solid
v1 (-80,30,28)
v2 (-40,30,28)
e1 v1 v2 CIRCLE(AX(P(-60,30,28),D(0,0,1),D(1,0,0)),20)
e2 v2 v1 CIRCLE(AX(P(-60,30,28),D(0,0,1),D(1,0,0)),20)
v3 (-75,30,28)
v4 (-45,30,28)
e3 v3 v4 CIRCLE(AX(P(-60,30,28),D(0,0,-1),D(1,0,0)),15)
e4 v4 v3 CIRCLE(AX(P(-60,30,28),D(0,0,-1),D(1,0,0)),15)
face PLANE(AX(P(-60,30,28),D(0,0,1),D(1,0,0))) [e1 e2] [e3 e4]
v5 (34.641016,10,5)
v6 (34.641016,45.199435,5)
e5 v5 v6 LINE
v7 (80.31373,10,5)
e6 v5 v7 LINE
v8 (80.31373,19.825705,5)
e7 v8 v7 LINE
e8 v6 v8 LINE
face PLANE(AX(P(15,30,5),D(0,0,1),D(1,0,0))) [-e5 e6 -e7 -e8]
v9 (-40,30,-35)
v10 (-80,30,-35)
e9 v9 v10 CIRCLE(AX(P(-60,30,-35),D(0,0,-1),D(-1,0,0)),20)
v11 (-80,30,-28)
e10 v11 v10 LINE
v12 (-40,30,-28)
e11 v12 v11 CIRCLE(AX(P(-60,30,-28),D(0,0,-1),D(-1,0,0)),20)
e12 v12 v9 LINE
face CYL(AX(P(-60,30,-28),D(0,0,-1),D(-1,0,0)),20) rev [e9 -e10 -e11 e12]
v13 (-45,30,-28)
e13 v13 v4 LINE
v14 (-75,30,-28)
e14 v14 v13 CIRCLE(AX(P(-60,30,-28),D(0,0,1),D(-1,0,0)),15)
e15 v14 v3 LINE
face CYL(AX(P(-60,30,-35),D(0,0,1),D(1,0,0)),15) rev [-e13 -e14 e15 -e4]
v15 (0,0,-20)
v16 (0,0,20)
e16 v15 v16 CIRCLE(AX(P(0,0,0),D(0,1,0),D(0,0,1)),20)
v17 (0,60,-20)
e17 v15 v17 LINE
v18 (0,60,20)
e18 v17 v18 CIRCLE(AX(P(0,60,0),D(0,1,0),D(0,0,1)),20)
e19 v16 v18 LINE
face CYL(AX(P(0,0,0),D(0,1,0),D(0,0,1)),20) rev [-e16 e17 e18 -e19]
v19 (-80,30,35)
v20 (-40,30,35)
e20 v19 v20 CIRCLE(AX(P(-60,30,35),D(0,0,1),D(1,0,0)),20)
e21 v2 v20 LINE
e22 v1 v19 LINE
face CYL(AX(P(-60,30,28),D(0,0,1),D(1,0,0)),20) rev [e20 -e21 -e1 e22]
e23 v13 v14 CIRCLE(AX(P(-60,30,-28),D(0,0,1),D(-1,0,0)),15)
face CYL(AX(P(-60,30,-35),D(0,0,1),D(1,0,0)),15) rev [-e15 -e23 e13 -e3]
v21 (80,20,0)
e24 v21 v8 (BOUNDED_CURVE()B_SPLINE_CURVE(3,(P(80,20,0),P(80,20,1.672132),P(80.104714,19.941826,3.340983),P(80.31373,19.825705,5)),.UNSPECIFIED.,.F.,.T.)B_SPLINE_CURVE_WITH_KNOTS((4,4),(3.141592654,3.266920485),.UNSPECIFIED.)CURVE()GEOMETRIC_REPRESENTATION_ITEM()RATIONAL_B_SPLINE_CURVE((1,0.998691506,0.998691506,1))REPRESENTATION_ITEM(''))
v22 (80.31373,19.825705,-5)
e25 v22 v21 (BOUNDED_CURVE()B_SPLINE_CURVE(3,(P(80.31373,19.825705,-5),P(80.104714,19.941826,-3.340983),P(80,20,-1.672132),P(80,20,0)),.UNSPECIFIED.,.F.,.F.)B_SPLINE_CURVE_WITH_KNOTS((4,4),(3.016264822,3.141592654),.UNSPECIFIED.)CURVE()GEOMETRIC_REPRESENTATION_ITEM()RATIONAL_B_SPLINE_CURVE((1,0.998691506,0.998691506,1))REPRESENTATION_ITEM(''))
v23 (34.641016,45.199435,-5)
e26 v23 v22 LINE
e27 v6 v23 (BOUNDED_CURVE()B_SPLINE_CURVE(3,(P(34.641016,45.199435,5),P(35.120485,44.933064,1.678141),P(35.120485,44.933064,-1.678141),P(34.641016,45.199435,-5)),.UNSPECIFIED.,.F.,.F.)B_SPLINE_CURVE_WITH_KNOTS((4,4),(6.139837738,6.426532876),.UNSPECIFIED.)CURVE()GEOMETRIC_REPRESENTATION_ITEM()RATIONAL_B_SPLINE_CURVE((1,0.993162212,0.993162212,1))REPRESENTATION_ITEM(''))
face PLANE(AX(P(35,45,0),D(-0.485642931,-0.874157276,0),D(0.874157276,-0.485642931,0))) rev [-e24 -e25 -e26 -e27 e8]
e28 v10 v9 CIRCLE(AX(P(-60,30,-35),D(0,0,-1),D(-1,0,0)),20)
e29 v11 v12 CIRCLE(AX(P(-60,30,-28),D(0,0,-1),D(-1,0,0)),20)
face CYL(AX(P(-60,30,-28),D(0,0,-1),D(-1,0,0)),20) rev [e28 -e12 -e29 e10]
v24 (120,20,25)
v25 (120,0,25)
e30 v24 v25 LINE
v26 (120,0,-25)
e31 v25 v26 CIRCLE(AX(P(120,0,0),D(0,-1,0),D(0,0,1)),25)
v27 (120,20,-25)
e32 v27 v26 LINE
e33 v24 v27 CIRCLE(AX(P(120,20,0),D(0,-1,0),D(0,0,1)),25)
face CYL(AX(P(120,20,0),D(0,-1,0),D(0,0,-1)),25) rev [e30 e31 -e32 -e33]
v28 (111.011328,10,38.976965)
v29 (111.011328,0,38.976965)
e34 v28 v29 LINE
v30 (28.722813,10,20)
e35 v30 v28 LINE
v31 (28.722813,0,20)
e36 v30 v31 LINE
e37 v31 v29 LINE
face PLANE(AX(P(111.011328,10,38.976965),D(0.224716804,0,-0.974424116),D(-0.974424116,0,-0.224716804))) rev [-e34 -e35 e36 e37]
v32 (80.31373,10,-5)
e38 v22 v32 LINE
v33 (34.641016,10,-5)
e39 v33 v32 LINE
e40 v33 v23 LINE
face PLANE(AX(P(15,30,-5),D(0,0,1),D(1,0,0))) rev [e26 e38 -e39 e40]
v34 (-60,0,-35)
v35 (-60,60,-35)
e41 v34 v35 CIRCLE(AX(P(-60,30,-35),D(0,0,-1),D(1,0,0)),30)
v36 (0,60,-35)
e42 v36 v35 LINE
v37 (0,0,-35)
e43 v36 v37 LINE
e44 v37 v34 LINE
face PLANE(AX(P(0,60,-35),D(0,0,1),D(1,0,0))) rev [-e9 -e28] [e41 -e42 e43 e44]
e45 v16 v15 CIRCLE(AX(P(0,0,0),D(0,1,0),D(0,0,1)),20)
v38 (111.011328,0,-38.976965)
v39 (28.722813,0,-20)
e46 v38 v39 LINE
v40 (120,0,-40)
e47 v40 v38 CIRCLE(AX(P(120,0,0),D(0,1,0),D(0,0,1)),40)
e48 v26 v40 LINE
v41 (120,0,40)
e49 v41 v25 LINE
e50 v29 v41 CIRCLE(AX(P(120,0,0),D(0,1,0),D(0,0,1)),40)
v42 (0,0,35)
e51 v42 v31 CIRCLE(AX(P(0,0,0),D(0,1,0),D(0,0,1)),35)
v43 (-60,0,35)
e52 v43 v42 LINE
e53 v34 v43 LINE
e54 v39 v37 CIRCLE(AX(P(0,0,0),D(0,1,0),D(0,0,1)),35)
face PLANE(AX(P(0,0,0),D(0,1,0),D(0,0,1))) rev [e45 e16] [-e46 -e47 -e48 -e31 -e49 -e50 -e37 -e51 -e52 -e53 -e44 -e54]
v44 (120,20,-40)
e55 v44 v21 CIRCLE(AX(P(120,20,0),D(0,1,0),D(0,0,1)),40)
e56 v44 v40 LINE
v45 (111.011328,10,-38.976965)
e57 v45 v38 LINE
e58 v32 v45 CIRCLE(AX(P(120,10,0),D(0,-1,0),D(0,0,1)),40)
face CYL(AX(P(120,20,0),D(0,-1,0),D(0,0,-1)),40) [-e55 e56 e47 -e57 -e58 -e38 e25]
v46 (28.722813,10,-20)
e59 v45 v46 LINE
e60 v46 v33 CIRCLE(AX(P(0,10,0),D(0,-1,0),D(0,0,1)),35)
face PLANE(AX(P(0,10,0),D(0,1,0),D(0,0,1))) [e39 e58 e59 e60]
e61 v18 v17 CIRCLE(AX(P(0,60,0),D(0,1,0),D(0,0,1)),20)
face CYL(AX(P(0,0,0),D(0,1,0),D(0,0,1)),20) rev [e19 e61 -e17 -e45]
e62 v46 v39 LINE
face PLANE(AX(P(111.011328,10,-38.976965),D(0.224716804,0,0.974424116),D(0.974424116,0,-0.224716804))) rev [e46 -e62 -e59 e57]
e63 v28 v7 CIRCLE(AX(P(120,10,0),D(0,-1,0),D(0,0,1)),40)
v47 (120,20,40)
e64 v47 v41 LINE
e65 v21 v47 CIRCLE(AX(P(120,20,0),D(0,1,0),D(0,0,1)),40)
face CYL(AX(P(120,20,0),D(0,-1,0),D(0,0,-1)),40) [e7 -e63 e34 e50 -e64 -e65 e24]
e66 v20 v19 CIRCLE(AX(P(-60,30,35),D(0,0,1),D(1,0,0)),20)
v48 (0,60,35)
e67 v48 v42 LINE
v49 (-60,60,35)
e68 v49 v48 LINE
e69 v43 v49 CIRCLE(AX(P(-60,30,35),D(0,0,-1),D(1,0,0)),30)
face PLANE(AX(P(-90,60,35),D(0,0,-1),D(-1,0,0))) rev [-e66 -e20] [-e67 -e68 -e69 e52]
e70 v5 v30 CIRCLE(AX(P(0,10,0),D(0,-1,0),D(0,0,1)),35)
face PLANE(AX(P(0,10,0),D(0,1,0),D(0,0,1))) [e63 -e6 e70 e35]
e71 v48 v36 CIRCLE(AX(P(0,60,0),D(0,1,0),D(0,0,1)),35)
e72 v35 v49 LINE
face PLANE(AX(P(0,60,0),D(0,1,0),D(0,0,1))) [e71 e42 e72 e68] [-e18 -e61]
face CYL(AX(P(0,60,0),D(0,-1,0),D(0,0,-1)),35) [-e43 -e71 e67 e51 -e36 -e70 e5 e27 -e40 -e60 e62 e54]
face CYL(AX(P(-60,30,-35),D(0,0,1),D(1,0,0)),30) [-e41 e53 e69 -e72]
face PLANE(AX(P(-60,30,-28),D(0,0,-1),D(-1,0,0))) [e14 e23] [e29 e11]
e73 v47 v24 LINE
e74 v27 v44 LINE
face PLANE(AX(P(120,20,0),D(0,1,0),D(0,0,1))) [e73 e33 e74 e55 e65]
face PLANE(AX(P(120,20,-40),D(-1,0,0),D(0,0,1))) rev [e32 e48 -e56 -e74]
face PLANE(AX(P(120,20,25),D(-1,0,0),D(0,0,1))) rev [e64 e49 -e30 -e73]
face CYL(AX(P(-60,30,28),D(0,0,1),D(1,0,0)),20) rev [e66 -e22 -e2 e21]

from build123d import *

# Parameters (mm, degrees)
BASE_BLOCK_DEPTH              = 60
BLOCK_SIDE_PROFILE_CUT_DEPTH  = 129.840987267
VERTICAL_BORE_SKETCH_R        = 20
VERTICAL_BORE_40_DEPTH        = 114.688170009
HORIZONTAL_BORE_SKETCH_R      = 15
HORIZONTAL_BORE_30_DEPTH      = 129.840987267
COUNTERBORE_SIDE_A_SKETCH_R   = 20
COUNTERBORE_SIDE_A_40X7_DEPTH = 7
COUNTERBORE_START             = -7
COUNTERBORE_SIDE_B_SKETCH_R   = 20
COUNTERBORE_SIDE_B_40X7_DEPTH = 7
FORK_ARM_DEPTH                = 20
ARM_WEB_PLATE_DEPTH           = 10
ARM_RIB_REACH                 = 142
ARM_RIB_SKETCH_WALL_W         = 333.478150704
ARM_RIB_SKETCH_WALL_H         = 10


with BuildPart() as part:
    # Base Block Sketch → Base Block (new body)
    with BuildSketch(Plane(origin=(0, 0, 0), x_dir=(1, 0, 0), z_dir=(0, 1, 0))):
        with BuildLine():
            Line((0, 35), (-90, 35))
            Line((-90, 35), (-90, -35))
            Line((-90, -35), (0, -35))
            ThreePointArc((0, -35), (35, 0), (0, 35))
        make_face()
    extrude(amount=BASE_BLOCK_DEPTH)

    # Block Side Profile Sketch → Block Side Profile Cut (cut, through all)
    with BuildSketch(Plane.XY.offset(35)):
        with BuildLine():
            Line((-60, 60), (-120, 60))
            Line((-120, 60), (-120, 0))
            Line((-120, 0), (-60, 0))
            ThreePointArc((-60, 0), (-90, 30), (-60, 60))
        make_face()
    extrude(amount=-BLOCK_SIDE_PROFILE_CUT_DEPTH, mode=Mode.SUBTRACT)

    # Vertical Bore Sketch → Vertical Bore Ø40 (cut, through all)
    with BuildSketch(Plane(origin=(0, 60, 0), x_dir=(1, 0, 0), z_dir=(0, 1, 0))):
        with Locations(Location((0, 0, 0), (0, 0, 270))):
            Circle(VERTICAL_BORE_SKETCH_R)
    extrude(amount=-VERTICAL_BORE_40_DEPTH, mode=Mode.SUBTRACT)

    # Horizontal Bore Sketch → Horizontal Bore Ø30 (cut, through all)
    with BuildSketch(Plane.XY.offset(35)):
        with Locations((-60, 30)):
            Circle(HORIZONTAL_BORE_SKETCH_R)
    extrude(amount=-HORIZONTAL_BORE_30_DEPTH, mode=Mode.SUBTRACT)

    # Counterbore Side A Sketch → Counterbore Side A Ø40x7 (cut)
    with BuildSketch(Plane.XY.offset(35)):
        with Locations((-60, 30)):
            Circle(COUNTERBORE_SIDE_A_SKETCH_R)
    extrude(amount=-COUNTERBORE_SIDE_A_40X7_DEPTH, mode=Mode.SUBTRACT)

    # Counterbore Side B Sketch → Counterbore Side B Ø40x7 (cut)
    with BuildSketch(Plane(origin=(0, 0, -35), x_dir=(-1, 0, 0), z_dir=(0, 0, -1)).offset(COUNTERBORE_START)):
        with Locations(Location((60, 30, 0), (0, 0, 180))):
            Circle(COUNTERBORE_SIDE_B_SKETCH_R)
    extrude(amount=COUNTERBORE_SIDE_B_40X7_DEPTH, mode=Mode.SUBTRACT)



with BuildPart() as body_2:
    # Fork Arm Sketch → Fork Arm (new body)
    with BuildSketch(Plane(origin=(0, 0, 0), x_dir=(1, 0, 0), z_dir=(0, 1, 0))):
        with BuildLine():
            Line((120, 40), (120, 25))
            ThreePointArc((120, 25), (95, 0), (120, -25))
            Line((120, -25), (120, -40))
            ThreePointArc((120, -40), (80, 0), (120, 40))
        make_face()
    extrude(amount=FORK_ARM_DEPTH)


with BuildPart() as part_1:
    add(part.part)

    add(body_2.part)  # Arm Web Plate merges body 2
    # Arm Web Plate Sketch → Arm Web Plate (add)
    with BuildSketch(Plane(origin=(0, 0, 0), x_dir=(1, 0, 0), z_dir=(0, 1, 0))):
        with BuildLine():
            Line((111.011327845, 38.976964644), (28.722813233, 20))
            ThreePointArc((28.722813233, 20), (35, 0), (28.722813233, -20))
            Line((28.722813233, -20), (111.011327845, -38.976964644))
            ThreePointArc((111.011327845, -38.976964644), (80, 0), (111.011327845, 38.976964644))
        make_face()
    extrude(amount=ARM_WEB_PLATE_DEPTH)

    # Arm Rib Sketch wall → Arm Rib (add, up to next)
    with BuildSketch(Plane(origin=(57.5, 32.5, 0), x_dir=(0.874157276122, -0.485642931179, 0), z_dir=(0.485642931179, 0.874157276122, 0)), mode=Mode.PRIVATE) as arm_rib_sk1:
        Rectangle(ARM_RIB_SKETCH_WALL_W, ARM_RIB_SKETCH_WALL_H)
    arm_rib_tool1 = extrude(arm_rib_sk1.sketch, amount=-ARM_RIB_REACH, mode=Mode.PRIVATE) - part_1.part
    add(arm_rib_tool1.solids().sort_by_distance((57.5, 32.5, 0))[0])


solid = part_1.part
